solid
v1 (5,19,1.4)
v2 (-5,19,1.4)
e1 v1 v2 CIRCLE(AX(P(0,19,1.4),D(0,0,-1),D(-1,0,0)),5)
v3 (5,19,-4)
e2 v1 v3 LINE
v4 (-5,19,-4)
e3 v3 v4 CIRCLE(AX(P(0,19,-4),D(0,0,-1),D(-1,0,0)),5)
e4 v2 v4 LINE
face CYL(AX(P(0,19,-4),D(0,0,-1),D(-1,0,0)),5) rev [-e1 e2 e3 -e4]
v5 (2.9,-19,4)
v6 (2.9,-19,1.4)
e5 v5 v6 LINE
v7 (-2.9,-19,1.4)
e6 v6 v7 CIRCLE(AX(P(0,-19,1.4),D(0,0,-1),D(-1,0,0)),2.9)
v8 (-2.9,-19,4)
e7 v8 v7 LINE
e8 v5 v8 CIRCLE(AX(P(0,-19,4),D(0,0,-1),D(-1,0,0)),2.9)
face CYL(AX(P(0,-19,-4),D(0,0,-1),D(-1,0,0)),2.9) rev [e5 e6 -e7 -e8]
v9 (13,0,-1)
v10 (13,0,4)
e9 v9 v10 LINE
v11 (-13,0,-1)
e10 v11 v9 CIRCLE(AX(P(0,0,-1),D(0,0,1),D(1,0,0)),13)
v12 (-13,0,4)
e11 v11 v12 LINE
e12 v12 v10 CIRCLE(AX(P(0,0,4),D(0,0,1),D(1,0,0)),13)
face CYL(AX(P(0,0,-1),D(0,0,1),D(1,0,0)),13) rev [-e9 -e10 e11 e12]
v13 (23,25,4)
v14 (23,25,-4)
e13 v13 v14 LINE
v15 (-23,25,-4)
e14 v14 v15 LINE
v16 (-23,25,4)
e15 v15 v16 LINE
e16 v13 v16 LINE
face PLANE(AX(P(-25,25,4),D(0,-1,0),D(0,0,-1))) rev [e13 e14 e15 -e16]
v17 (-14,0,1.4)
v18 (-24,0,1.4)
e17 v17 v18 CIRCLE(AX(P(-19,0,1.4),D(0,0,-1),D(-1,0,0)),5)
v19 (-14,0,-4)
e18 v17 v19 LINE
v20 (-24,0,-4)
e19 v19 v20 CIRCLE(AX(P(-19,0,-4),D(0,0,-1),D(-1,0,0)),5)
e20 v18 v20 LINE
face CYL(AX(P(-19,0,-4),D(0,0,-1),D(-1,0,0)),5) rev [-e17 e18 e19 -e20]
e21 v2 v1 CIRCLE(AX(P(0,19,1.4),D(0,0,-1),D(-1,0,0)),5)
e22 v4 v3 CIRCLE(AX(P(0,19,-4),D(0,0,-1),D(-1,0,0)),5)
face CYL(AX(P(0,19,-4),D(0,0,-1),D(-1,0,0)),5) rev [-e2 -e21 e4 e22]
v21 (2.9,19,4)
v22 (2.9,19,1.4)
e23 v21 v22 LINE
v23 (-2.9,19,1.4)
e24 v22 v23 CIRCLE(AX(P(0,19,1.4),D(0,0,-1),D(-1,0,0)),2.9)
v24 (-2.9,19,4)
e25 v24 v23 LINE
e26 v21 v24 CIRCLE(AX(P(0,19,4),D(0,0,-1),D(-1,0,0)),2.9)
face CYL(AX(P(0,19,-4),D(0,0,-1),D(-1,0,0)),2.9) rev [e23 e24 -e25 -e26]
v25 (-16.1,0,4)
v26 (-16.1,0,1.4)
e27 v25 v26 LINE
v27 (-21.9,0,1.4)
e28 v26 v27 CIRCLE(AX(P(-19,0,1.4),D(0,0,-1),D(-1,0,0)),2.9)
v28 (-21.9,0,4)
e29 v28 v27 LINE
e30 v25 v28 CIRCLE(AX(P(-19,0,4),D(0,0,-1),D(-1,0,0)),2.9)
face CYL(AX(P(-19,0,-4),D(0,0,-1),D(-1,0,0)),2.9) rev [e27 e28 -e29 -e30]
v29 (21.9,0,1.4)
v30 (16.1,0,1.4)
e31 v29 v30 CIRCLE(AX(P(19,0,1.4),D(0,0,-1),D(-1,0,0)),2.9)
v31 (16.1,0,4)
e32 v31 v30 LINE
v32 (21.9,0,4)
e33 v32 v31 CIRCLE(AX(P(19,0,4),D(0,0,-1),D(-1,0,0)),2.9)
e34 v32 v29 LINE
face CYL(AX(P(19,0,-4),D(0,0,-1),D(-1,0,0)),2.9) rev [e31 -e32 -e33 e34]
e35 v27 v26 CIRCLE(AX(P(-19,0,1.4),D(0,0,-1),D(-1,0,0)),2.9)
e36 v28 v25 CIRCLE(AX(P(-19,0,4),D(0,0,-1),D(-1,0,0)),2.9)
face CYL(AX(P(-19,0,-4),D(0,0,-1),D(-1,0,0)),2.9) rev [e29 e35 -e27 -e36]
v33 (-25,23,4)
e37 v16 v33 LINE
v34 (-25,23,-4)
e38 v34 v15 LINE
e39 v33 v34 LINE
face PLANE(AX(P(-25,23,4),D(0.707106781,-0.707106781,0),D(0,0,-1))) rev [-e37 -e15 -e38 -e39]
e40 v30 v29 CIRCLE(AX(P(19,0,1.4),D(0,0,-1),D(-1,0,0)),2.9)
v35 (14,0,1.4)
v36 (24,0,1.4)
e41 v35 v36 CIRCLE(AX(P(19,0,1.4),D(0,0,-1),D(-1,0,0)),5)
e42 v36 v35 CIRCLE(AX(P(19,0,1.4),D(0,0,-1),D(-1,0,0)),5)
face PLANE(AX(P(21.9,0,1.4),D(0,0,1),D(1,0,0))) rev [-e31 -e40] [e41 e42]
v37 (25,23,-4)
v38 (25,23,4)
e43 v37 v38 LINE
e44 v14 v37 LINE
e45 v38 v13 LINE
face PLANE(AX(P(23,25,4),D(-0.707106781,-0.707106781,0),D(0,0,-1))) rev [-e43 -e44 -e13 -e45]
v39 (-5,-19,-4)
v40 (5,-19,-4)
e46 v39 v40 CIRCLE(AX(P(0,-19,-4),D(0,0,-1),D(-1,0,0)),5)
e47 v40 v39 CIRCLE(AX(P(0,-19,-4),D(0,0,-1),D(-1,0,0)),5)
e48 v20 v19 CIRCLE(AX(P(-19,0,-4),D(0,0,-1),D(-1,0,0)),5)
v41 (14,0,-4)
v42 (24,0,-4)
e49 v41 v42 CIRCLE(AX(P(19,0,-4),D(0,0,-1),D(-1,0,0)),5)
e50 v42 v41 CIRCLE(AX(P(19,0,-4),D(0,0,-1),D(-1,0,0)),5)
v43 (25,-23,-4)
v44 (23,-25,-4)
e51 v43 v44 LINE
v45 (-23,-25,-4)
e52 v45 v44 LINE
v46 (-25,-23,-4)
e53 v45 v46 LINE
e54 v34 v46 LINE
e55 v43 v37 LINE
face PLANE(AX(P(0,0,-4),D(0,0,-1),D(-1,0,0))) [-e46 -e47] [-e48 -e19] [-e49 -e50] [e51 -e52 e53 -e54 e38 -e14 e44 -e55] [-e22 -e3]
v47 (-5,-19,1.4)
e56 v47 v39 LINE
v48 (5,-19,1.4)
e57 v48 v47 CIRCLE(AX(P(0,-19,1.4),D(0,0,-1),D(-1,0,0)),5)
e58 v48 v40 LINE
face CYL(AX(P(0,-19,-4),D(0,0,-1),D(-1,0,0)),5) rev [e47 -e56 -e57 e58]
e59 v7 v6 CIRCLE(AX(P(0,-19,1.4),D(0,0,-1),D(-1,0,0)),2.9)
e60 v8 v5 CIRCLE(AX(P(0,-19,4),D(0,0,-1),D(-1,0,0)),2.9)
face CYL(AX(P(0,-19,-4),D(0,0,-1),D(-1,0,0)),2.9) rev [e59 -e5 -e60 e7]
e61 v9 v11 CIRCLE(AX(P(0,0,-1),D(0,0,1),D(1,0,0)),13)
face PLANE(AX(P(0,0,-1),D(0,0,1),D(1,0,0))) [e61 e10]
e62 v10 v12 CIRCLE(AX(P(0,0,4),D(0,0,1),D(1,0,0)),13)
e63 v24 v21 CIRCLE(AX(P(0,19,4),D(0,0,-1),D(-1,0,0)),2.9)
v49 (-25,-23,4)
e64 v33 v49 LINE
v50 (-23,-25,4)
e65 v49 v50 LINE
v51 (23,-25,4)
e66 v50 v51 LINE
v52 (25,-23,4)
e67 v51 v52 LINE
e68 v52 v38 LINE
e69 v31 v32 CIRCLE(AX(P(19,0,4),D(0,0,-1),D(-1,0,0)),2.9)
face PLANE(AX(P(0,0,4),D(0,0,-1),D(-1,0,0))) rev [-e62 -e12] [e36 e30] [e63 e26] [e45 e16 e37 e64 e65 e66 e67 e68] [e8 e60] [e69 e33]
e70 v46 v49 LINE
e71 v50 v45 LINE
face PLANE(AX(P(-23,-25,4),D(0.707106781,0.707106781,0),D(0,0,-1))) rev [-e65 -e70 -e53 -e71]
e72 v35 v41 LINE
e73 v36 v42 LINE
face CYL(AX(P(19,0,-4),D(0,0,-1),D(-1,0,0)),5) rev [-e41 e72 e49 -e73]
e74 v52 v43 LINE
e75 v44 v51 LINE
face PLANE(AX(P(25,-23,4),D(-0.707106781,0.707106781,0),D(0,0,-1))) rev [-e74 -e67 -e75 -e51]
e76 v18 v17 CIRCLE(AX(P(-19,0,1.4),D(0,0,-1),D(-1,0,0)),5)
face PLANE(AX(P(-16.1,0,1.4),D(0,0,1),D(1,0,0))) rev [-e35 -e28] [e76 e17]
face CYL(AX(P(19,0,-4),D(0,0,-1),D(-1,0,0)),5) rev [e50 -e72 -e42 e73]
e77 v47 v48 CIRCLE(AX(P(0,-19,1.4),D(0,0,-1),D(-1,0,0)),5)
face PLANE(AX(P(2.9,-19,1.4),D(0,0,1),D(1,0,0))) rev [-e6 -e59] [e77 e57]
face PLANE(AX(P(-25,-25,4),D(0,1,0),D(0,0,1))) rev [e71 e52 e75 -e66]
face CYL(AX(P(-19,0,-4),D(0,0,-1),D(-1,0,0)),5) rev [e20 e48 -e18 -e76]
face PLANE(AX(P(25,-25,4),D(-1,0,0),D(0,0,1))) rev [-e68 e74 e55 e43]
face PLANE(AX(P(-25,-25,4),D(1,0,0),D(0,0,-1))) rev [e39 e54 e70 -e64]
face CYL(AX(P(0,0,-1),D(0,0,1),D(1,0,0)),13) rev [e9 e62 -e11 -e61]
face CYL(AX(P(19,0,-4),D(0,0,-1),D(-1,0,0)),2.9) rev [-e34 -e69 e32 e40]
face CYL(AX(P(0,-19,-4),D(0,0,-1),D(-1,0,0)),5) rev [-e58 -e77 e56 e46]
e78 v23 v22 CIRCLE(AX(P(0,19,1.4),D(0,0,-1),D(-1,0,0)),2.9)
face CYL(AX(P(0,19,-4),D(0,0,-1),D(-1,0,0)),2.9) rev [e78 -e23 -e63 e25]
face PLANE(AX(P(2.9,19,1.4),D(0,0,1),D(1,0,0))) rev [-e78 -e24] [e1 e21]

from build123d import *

# Parameters (mm, degrees)
SKETCH_1_W                   = 50
SKETCH_1_H                   = 50
EXTRUDE_1_DEPTH              = 4
SKETCH_2_R                   = 13
CUT_EXTRUDE_1_DEPTH          = 5
HOLE_WIZARD_M5_1_D           = 5.8
HOLE_WIZARD_M5_1_CBORE_D     = 10
HOLE_WIZARD_M5_1_CBORE_DEPTH = 5.4
CHAMFER_1_SIZE               = 2


with BuildPart() as part:
    # 草图1 → 凸台-拉伸1 (new, symmetric)
    with BuildSketch(Plane.XY):
        Rectangle(SKETCH_1_W, SKETCH_1_H)
    extrude(amount=EXTRUDE_1_DEPTH, both=True)

    # 草图2 → 切除-拉伸1 (cut)
    with BuildSketch(Plane.XY.offset(4)):
        Circle(SKETCH_2_R)
    extrude(amount=-CUT_EXTRUDE_1_DEPTH, mode=Mode.SUBTRACT)

    # M5 六角凹头螺钉的柱形沉头孔1 (through all)
    with Locations(Plane(origin=(0, 0, -4), x_dir=(1, 0, 0), z_dir=(0, 0, -1))):
        with Locations((-19, 0), (0, -19), (19, 0), (0, 19)):
            CounterBoreHole(HOLE_WIZARD_M5_1_D / 2, HOLE_WIZARD_M5_1_CBORE_D / 2, HOLE_WIZARD_M5_1_CBORE_DEPTH)

    # 倒角1
    chamfer_1_edges = [part.edges().sort_by_distance(p)[0] for p in [
        (25, -25, 0),
        (-25, -25, 0),
        (-25, 25, 0),
        (25, 25, 0),
    ]]
    chamfer(chamfer_1_edges, length=CHAMFER_1_SIZE)


solid = part.part
